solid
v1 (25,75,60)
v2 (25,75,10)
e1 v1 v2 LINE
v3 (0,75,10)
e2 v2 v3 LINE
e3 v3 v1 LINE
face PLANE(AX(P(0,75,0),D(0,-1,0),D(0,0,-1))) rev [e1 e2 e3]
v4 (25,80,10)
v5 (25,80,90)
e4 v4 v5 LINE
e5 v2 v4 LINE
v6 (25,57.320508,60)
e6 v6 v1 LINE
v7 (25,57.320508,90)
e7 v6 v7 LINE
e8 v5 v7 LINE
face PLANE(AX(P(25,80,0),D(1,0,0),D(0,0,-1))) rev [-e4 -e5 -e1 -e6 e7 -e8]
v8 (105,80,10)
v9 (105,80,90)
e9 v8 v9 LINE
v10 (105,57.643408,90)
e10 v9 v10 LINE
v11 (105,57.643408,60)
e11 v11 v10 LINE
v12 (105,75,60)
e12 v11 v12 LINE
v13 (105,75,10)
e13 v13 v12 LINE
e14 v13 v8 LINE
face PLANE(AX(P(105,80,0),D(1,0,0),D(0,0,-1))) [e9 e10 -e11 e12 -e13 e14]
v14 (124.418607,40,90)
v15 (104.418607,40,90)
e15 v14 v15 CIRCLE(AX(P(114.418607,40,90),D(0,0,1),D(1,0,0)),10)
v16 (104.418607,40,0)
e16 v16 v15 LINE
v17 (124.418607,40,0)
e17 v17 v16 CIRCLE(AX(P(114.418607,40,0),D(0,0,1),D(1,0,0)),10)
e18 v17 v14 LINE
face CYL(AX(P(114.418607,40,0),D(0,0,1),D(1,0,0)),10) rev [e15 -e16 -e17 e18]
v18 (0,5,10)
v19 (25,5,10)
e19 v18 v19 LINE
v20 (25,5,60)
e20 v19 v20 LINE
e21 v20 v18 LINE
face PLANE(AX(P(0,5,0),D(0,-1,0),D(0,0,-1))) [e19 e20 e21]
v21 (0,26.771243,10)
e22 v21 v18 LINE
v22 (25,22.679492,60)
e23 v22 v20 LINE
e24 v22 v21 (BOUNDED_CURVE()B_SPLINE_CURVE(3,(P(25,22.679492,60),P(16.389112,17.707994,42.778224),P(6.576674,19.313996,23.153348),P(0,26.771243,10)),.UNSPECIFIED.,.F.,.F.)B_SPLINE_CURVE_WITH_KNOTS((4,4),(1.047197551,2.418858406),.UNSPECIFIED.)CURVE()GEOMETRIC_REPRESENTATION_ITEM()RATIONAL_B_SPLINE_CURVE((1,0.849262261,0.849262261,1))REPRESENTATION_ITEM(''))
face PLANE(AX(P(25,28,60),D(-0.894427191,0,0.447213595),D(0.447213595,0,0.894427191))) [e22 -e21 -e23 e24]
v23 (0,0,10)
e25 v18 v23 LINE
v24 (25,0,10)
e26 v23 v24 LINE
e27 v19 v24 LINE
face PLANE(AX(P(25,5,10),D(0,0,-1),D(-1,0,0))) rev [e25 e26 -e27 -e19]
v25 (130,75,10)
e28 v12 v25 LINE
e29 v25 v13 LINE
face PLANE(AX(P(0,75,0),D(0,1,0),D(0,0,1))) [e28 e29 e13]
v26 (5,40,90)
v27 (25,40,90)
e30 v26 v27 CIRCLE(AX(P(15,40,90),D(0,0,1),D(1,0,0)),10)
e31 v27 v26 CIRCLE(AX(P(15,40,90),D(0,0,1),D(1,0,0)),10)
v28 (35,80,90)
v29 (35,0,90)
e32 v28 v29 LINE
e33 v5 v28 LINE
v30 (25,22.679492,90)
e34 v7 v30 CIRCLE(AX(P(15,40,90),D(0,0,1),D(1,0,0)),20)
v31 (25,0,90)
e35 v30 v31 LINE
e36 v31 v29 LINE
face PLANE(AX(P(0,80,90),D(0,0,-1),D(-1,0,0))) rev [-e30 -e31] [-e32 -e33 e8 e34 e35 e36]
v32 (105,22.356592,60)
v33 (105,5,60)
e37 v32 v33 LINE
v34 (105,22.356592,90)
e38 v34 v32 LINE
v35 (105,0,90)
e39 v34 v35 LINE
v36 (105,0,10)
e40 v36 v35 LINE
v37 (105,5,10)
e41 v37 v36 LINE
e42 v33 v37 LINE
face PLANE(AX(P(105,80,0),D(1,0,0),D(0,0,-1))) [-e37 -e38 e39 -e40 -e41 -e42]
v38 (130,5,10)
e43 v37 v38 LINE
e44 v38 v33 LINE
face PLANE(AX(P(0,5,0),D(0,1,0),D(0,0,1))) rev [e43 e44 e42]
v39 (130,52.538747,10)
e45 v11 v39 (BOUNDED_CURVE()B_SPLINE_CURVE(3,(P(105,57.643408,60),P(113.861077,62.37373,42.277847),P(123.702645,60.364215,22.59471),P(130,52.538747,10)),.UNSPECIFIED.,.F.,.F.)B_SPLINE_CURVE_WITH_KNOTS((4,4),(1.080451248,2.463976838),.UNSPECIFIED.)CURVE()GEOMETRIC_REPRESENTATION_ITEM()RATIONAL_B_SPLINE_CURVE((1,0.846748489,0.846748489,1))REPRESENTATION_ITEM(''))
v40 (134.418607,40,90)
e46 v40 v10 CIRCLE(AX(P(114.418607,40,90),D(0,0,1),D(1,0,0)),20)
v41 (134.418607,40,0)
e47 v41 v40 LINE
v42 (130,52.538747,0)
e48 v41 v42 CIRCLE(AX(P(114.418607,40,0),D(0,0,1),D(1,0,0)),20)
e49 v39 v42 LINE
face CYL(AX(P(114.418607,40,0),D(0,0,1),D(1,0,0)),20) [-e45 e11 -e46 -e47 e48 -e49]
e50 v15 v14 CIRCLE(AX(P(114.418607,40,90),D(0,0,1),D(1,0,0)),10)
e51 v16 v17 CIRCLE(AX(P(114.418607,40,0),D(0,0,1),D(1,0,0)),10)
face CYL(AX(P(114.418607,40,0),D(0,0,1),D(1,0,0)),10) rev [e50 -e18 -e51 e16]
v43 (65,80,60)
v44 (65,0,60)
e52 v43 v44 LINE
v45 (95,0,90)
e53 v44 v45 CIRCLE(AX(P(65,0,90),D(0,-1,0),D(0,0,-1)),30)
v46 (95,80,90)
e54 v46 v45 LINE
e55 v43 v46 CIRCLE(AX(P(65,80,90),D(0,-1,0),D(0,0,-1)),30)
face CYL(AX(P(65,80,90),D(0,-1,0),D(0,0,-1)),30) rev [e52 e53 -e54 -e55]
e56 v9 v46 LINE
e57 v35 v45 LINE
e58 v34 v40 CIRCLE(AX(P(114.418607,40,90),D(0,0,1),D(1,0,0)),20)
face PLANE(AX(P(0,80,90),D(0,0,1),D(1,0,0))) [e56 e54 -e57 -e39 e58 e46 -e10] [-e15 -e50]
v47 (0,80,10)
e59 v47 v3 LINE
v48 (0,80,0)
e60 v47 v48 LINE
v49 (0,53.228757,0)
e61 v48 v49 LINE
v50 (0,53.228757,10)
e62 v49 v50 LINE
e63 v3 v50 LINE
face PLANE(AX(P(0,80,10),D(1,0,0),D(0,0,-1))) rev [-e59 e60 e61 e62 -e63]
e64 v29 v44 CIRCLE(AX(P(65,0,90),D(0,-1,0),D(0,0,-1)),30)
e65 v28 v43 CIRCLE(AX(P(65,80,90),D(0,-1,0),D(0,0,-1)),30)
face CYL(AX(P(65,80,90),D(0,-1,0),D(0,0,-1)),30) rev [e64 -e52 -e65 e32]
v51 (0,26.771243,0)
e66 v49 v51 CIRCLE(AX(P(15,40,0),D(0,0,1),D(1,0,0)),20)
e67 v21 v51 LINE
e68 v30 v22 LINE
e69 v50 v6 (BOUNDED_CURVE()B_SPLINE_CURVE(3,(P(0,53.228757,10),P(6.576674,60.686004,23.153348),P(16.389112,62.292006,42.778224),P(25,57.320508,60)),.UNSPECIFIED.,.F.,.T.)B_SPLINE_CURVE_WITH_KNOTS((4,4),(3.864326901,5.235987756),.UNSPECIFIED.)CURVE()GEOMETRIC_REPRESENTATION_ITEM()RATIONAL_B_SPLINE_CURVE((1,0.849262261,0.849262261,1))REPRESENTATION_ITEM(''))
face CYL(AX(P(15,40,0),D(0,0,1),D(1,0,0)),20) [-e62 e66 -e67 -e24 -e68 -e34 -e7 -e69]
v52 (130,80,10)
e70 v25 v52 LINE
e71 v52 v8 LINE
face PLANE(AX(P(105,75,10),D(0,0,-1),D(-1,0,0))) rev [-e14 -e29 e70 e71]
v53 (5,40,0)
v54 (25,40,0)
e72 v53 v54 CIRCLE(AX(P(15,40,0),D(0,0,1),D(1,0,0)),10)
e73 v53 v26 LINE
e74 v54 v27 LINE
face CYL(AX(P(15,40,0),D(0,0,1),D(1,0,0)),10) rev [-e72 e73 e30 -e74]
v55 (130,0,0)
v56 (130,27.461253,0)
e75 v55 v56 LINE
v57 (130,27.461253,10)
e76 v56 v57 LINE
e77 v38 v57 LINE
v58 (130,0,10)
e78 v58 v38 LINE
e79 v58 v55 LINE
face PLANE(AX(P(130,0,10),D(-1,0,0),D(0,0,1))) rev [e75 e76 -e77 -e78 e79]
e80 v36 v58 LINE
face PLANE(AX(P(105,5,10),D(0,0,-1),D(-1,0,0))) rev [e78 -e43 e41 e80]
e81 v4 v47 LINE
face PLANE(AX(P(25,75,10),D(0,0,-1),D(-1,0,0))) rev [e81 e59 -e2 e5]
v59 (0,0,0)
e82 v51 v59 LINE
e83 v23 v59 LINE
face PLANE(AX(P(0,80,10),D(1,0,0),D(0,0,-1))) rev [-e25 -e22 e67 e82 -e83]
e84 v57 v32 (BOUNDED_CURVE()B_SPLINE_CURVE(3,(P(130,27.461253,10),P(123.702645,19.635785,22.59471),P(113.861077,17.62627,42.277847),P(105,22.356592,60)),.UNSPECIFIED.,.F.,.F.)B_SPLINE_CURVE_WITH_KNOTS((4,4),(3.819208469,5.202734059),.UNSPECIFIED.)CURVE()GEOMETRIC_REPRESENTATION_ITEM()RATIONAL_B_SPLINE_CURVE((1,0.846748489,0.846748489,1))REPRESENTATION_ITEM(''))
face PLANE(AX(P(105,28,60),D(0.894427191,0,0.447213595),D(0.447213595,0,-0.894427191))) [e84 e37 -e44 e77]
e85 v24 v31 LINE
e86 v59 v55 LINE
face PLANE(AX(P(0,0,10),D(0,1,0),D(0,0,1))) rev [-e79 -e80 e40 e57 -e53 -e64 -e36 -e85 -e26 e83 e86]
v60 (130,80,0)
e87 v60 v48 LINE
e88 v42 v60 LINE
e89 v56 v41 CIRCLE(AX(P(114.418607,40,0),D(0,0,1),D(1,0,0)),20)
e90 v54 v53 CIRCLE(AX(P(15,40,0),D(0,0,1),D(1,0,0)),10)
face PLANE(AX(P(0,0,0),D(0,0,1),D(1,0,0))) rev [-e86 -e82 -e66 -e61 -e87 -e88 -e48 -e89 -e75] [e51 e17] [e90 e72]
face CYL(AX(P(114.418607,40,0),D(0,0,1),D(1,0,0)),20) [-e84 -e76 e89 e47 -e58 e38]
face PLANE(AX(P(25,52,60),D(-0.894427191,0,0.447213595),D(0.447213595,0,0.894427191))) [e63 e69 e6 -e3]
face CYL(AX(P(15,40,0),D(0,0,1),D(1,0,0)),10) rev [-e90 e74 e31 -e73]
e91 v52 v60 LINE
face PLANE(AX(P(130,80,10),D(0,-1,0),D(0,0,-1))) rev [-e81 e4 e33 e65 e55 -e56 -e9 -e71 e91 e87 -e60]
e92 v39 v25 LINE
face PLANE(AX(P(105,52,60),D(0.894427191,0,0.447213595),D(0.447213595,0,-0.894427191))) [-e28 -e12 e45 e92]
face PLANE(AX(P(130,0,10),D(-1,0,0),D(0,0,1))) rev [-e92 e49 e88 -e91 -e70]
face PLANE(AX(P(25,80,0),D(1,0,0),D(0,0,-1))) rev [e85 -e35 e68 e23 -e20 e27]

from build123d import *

# Parameters (mm, degrees)
BASE_PLATE_SKETCH_W    = 130
BASE_PLATE_SKETCH_H    = 80
BASE_PLATE_10MM_DEPTH  = 10
MAIN_BODY_PROFILE_W    = 10
MAIN_BODY_PROFILE_H    = 80
MAIN_BODY_DEPTH        = 80
SIDE_WALL_A_DEPTH      = 90
SIDE_WALL_B_DEPTH      = 90
HALF_BORE_SKETCH_R     = 10
HALF_BORE_CUT_DEPTH    = 90
RIB_A_DEPTH            = 28
RIB_B_DEPTH            = 28
BOSS_DEPTH             = 28
RECESS_CUT_A_5MM_DEPTH = 5
RECESS_CUT_B_5MM_DEPTH = 5


with BuildPart() as part:
    # Base Plate Sketch → Base Plate 10mm (new body)
    with BuildSketch(Plane.XY):
        with Locations((65, 40)):
            Rectangle(BASE_PLATE_SKETCH_W, BASE_PLATE_SKETCH_H)
    extrude(amount=BASE_PLATE_10MM_DEPTH)

    # Main Body Profile → Main Body (add)
    with BuildSketch(Plane.XZ):
        with Locations((30, 50)):
            Rectangle(MAIN_BODY_PROFILE_W, MAIN_BODY_PROFILE_H)
        with BuildLine():
            Line((35, 10), (65, 10))
            Line((65, 10), (95, 10))
            Line((95, 10), (95, 90))
            ThreePointArc((95, 90), (65, 60), (35, 90))
            Line((35, 90), (35, 10))
        make_face()
        with Locations((100, 50)):
            Rectangle(MAIN_BODY_PROFILE_W, MAIN_BODY_PROFILE_H)
    extrude(amount=-MAIN_BODY_DEPTH)

    # Side Wall A Sketch → Side Wall A (add)
    with BuildSketch(Plane.XY.offset(90)):
        with BuildLine():
            Line((105, 57.643408065), (105, 22.356591935))
            ThreePointArc((105, 22.356591935), (134.418606683, 40), (105, 57.643408065))
        make_face()
    extrude(amount=-SIDE_WALL_A_DEPTH)

    # Side Wall B Sketch → Side Wall B (add)
    with BuildSketch(Plane.XY.offset(90)):
        with BuildLine():
            Line((25, 57.320508076), (25, 22.679491924))
            ThreePointArc((25, 22.679491924), (-5, 40), (25, 57.320508076))
        make_face()
    extrude(amount=-SIDE_WALL_B_DEPTH)

    # Half Bore Sketch → Half Bore Cut (cut)
    with BuildSketch(Plane.XY.offset(90)):
        with Locations((114.418606683, 40)):
            Circle(HALF_BORE_SKETCH_R)
        with Locations((15, 40)):
            Circle(HALF_BORE_SKETCH_R)
    extrude(amount=-HALF_BORE_CUT_DEPTH, mode=Mode.SUBTRACT)

    # Rib A Sketch → Rib A (add)
    with BuildSketch(Plane.XZ):
        Polygon((105, 10), (105, 60), (130, 10), align=None)
    extrude(amount=-RIB_A_DEPTH)

    # Rib B Sketch → Rib B (add)
    with BuildSketch(Plane.XZ):
        Polygon((25, 10), (25, 60), (0, 10), align=None)
    extrude(amount=-RIB_B_DEPTH)

    # Boss Sketch → Boss (add)
    with BuildSketch(Plane(origin=(0, 80, 0), x_dir=(1, 0, 0), z_dir=(0, 1, 0))):
        Polygon((105, -10), (105, -60), (130, -10), align=None)
        Polygon((25, -10), (25, -60), (0, -10), align=None)
    extrude(amount=-BOSS_DEPTH)

    # Recess A Sketch → Recess Cut A 5mm (cut)
    with BuildSketch(Plane.XZ):
        Polygon((25, 60), (25, 10), (0, 10), align=None)
        Polygon((105, 60), (105, 10), (130, 10), align=None)
    extrude(amount=-RECESS_CUT_A_5MM_DEPTH, mode=Mode.SUBTRACT)

    # Recess B Sketch → Recess Cut B 5mm (cut)
    with BuildSketch(Plane(origin=(0, 80, 0), x_dir=(1, 0, 0), z_dir=(0, 1, 0))):
        Polygon((25, -60), (25, -10), (0, -10), align=None)
        Polygon((105, -60), (105, -10), (130, -10), align=None)
    extrude(amount=-RECESS_CUT_B_5MM_DEPTH, mode=Mode.SUBTRACT)


solid = part.part
